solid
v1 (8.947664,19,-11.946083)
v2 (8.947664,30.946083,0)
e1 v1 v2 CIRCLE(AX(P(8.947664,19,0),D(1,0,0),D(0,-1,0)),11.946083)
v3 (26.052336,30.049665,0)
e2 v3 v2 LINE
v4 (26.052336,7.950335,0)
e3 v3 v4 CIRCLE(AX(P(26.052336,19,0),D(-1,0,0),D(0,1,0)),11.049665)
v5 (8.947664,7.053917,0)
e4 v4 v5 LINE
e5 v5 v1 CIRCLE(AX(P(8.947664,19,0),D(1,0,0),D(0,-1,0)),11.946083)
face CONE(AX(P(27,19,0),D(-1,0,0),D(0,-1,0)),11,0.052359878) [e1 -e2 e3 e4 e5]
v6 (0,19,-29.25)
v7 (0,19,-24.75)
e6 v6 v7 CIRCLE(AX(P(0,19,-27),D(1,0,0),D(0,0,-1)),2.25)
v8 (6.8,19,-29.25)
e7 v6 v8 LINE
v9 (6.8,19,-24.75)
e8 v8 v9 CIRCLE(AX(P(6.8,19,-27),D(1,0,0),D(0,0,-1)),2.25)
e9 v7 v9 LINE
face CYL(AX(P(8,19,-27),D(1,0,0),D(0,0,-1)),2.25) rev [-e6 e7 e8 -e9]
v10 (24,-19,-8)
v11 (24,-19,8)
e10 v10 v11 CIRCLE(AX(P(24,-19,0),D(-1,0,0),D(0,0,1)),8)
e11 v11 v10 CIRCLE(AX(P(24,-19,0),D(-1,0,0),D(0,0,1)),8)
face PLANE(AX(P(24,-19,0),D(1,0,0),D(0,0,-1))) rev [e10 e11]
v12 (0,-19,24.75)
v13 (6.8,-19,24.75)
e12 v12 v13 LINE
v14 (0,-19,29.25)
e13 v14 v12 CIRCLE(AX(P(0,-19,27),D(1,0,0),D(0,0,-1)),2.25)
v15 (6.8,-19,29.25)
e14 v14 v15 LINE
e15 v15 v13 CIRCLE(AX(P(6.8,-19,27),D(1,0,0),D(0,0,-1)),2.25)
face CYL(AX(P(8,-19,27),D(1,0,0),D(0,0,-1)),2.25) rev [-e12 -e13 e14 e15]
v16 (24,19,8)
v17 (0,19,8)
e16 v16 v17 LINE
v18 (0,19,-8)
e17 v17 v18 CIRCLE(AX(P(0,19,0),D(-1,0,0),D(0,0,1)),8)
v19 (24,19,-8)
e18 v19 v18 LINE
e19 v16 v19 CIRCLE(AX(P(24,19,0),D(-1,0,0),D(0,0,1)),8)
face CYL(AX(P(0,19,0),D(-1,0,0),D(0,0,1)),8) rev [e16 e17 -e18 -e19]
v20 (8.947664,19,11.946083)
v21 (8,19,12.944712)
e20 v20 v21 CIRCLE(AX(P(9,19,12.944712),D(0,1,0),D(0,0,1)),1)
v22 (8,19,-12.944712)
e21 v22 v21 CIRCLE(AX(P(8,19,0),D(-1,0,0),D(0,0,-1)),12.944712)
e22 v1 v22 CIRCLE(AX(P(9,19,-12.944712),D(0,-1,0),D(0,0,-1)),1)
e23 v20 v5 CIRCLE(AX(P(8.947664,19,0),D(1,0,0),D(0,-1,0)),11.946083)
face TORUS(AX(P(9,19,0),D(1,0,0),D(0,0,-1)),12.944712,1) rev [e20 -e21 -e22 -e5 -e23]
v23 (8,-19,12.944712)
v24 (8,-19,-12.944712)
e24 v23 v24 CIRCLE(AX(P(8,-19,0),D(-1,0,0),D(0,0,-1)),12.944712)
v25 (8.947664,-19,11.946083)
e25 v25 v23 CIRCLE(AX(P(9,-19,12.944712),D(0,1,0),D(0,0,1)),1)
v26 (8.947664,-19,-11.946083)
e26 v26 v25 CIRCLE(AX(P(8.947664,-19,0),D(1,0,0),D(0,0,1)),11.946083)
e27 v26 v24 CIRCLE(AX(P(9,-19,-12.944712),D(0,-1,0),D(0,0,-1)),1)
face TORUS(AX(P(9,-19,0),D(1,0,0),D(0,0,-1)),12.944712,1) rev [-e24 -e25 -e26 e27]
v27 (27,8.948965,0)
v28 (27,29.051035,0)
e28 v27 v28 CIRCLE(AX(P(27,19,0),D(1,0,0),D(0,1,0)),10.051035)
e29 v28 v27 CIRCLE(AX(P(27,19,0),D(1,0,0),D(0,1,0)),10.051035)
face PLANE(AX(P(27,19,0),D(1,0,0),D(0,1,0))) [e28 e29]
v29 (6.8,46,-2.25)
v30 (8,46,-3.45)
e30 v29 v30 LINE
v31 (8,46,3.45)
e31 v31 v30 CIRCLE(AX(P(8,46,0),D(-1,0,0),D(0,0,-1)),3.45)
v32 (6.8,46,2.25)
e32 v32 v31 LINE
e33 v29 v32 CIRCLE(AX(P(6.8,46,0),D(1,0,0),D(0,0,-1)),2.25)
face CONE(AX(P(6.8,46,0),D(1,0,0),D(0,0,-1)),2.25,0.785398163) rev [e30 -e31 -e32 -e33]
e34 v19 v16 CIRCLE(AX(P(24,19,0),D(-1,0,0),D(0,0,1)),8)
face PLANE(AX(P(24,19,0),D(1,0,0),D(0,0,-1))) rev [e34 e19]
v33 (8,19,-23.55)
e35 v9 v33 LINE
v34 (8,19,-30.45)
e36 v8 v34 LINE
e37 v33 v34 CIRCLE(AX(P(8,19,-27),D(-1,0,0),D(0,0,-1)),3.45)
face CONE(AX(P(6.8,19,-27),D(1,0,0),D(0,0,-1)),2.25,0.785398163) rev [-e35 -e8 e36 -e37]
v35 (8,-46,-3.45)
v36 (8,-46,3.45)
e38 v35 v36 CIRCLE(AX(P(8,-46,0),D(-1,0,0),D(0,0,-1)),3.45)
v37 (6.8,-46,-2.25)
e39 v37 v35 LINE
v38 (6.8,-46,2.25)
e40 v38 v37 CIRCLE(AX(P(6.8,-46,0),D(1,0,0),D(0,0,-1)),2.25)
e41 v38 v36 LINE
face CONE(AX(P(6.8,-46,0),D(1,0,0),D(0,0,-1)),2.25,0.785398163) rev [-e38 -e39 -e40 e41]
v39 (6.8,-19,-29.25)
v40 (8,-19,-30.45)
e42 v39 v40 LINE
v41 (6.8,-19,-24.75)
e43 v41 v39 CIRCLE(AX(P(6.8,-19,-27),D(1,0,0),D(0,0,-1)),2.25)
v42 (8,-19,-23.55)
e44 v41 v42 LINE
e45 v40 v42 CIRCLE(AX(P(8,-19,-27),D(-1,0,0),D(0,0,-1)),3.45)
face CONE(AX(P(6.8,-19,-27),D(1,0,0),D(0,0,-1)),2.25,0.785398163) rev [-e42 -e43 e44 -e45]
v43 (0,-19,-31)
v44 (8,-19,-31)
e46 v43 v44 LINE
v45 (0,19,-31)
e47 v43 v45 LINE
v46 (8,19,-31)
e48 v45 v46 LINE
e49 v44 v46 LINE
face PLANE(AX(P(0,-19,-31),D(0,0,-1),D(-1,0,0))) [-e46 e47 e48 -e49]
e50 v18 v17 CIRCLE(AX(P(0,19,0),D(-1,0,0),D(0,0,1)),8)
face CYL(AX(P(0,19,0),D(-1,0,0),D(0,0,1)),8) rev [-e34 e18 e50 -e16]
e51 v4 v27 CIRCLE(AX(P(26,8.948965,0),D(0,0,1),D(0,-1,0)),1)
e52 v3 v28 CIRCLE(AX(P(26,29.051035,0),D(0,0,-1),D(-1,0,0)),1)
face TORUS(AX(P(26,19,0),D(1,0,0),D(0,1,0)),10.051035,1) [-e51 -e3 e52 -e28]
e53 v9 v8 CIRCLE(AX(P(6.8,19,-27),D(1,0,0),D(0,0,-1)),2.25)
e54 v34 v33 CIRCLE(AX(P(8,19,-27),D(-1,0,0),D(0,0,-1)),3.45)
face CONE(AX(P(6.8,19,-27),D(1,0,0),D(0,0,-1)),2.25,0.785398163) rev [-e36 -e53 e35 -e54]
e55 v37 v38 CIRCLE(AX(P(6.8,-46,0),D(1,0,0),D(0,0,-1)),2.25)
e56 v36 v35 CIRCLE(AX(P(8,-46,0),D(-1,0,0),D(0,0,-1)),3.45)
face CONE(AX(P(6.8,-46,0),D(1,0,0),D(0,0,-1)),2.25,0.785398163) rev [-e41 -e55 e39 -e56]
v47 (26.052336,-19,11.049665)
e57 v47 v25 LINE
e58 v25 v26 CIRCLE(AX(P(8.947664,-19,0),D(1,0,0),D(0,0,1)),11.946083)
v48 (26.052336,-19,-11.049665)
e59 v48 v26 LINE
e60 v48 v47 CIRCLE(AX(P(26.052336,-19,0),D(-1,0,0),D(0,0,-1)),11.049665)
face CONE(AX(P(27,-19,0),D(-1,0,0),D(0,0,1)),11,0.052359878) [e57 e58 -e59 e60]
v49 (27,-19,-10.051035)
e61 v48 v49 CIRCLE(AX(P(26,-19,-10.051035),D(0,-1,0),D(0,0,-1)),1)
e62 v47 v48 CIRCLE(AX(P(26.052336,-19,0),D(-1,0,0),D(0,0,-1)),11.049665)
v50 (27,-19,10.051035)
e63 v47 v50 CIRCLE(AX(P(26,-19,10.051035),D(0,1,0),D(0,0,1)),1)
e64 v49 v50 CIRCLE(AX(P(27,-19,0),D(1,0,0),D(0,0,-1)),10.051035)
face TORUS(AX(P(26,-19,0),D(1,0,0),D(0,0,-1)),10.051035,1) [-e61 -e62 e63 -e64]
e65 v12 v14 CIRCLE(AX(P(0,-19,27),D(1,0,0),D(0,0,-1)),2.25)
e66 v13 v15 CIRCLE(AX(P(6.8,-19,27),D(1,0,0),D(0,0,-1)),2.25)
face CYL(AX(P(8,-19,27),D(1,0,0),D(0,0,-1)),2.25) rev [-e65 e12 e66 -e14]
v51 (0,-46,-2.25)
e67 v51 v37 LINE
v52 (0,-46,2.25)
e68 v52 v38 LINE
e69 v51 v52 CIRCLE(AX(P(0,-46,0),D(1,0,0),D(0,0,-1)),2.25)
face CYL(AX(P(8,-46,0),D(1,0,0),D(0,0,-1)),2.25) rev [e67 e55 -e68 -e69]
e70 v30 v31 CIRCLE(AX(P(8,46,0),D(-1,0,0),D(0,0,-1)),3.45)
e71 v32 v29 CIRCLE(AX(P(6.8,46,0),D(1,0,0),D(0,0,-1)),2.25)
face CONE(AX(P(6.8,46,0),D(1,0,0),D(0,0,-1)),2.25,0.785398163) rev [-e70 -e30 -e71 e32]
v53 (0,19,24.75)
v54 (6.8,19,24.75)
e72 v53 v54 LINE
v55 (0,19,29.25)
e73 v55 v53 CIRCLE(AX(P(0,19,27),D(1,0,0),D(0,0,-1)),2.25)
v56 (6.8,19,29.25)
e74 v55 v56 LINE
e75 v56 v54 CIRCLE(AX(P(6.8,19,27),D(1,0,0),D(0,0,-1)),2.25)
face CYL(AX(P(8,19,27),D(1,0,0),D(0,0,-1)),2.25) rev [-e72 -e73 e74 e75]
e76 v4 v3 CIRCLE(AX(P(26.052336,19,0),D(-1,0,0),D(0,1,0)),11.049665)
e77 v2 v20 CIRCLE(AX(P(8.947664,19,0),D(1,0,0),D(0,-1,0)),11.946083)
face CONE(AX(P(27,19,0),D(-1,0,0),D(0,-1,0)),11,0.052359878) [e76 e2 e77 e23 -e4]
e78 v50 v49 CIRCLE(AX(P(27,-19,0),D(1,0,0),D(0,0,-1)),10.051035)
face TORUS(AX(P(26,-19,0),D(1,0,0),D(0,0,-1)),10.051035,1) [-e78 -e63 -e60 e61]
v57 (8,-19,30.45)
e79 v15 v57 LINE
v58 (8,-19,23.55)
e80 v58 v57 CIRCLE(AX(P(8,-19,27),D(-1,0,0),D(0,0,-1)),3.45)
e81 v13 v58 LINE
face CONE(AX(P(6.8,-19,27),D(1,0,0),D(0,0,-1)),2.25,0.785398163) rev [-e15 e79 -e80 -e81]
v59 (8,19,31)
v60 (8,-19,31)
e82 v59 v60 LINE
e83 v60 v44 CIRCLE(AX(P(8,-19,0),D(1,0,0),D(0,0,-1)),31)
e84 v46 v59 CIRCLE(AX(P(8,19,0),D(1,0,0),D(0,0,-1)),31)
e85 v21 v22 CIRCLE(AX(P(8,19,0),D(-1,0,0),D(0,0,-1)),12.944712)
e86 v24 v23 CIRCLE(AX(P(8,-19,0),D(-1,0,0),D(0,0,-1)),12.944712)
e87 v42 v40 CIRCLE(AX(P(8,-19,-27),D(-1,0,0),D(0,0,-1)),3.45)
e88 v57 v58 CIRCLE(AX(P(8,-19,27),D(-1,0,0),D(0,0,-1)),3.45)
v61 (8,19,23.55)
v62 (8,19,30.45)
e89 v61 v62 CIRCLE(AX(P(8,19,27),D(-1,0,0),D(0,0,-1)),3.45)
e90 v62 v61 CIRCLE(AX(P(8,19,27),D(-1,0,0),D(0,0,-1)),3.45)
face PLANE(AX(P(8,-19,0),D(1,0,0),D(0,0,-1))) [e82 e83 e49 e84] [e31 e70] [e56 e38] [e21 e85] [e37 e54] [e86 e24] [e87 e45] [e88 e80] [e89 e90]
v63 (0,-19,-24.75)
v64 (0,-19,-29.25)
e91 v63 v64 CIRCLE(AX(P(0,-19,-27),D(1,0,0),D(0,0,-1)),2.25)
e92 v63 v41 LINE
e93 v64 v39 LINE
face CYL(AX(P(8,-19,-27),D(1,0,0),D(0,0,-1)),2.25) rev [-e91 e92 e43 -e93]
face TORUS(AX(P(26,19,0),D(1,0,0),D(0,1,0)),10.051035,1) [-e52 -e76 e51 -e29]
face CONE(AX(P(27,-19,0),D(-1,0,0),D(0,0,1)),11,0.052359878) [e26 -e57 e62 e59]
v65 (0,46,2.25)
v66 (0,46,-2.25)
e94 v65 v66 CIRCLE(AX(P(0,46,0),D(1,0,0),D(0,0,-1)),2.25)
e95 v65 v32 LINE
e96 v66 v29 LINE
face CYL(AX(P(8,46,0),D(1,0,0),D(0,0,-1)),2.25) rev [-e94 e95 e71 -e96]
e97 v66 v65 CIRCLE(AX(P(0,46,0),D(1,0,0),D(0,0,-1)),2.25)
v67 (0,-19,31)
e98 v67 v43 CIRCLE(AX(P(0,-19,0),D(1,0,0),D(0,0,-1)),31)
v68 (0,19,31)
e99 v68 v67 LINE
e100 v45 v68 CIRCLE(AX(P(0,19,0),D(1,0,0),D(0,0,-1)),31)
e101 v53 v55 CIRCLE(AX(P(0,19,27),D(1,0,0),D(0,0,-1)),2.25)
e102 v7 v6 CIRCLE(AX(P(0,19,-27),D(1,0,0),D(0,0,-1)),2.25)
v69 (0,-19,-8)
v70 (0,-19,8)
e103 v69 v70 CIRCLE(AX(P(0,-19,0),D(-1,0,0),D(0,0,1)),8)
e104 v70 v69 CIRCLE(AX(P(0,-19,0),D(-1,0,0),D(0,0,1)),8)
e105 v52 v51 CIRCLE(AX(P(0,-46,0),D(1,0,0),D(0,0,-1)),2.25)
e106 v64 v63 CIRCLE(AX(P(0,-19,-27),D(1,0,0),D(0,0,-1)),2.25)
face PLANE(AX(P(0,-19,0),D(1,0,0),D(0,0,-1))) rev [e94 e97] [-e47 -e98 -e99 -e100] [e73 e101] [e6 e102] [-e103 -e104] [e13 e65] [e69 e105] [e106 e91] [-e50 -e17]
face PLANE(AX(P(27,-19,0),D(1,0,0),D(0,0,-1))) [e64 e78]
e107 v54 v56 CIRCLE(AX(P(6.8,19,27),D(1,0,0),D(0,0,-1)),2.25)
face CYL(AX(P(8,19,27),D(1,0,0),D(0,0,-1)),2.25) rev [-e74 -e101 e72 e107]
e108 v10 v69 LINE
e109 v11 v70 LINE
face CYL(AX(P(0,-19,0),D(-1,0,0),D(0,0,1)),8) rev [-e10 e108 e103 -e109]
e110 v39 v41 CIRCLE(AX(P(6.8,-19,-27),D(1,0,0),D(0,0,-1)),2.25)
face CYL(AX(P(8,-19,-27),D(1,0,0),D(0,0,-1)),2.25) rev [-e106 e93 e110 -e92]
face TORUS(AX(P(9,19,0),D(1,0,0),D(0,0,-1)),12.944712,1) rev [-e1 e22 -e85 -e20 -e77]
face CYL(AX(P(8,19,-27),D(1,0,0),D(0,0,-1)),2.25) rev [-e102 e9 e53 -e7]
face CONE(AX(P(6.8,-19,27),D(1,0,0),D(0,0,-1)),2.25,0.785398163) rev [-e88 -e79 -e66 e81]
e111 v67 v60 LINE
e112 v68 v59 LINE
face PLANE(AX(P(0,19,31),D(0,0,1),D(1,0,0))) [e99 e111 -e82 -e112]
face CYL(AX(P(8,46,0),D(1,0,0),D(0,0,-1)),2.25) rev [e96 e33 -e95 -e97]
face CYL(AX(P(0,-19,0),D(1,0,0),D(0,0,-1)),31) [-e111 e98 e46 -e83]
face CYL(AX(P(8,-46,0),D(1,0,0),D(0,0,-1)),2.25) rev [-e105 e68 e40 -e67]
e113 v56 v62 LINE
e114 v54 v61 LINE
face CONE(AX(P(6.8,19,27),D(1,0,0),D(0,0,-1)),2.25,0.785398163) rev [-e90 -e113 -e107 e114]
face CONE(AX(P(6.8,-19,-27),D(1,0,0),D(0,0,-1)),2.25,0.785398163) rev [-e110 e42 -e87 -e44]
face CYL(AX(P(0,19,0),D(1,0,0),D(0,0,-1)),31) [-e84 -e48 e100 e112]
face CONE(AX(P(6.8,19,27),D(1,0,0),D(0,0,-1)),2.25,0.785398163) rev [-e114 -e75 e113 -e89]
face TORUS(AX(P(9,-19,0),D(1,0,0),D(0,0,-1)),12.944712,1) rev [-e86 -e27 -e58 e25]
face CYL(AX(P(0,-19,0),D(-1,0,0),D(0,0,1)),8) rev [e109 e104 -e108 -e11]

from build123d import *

# Parameters (mm, degrees)
BOSS_EXTRUDE1_DEPTH            = 8
F_16_0_16_DIAMETER_HOLE1_D     = 16
F_16_0_16_DIAMETER_HOLE1_DEPTH = 24
F_4_5_4_5_DIAMETER_HOLE1_D     = 4.5
CHAMFER1_SIZE                  = 1.2
FILLET1_R                      = 1


with BuildPart() as part:
    # Sketch1 → Boss-Extrude1 (new body)
    with BuildSketch(Plane(origin=(8, 0, 0), x_dir=(0, 0, -1), z_dir=(1, 0, 0))):
        with BuildLine():
            Line((31, -19), (31, 19))
            ThreePointArc((31, 19), (0, 50), (-31, 19))
            Line((-31, 19), (-31, -19))
            ThreePointArc((-31, -19), (0, -50), (31, -19))
        make_face()
    extrude(amount=-BOSS_EXTRUDE1_DEPTH)

    # Sketch2 → Revolve1 (revolve)
    with BuildSketch(Plane.XY, mode=Mode.PRIVATE) as revolve1_sk:
        Polygon((8, -7.004252194), (8, -19), (27, -19), (27, -8), align=None)
    revolve(revolve1_sk.sketch.rotate(Axis((8, -19, 0), (1, 0, 0)), 270), axis=Axis((8, -19, 0), (1, 0, 0)))

    # Sketch3 → Revolve2 (revolve)
    with BuildSketch(Plane.XY, mode=Mode.PRIVATE) as revolve2_sk:
        Polygon((8, 30.995747806), (8, 19), (27, 19), (27, 30), align=None)
    revolve(revolve2_sk.sketch.rotate(Axis((8, 19, 0), (1, 0, 0)), 270), axis=Axis((8, 19, 0), (1, 0, 0)))

    # Ø16.0 (16) Diameter Hole1
    with Locations(Plane.ZY):
        with Locations((0, 19), (0, -19)):
            Hole(F_16_0_16_DIAMETER_HOLE1_D / 2, depth=F_16_0_16_DIAMETER_HOLE1_DEPTH)

    # Ø4.5 (4.5) Diameter Hole1 (through all)
    with Locations(Plane(origin=(8, 0, 0), x_dir=(0, 0, -1), z_dir=(1, 0, 0))):
        with Locations((0, 46), (-27, 19), (27, 19), (-27, -19), (27, -19), (0, -46)):
            Hole(F_4_5_4_5_DIAMETER_HOLE1_D / 2)

    # Chamfer1
    chamfer1_edges = [part.edges().sort_by_distance(p)[0] for p in [
        (8, -46, -2.25),
        (8, -19, -29.25),
        (8, -19, 24.75),
        (8, 19, -29.25),
        (8, 19, 24.75),
        (8, 46, -2.25),
    ]]
    chamfer(chamfer1_edges, length=CHAMFER1_SIZE)

    # Fillet1
    fillet1_edges = [part.edges().sort_by_distance(p)[0] for p in [
        (8, -19, 11.995747806),
        (27, -19, 11),
        (8, 19, 11.995747806),
        (27, 19, 11),
    ]]
    fillet(fillet1_edges, radius=FILLET1_R)


solid = part.part
